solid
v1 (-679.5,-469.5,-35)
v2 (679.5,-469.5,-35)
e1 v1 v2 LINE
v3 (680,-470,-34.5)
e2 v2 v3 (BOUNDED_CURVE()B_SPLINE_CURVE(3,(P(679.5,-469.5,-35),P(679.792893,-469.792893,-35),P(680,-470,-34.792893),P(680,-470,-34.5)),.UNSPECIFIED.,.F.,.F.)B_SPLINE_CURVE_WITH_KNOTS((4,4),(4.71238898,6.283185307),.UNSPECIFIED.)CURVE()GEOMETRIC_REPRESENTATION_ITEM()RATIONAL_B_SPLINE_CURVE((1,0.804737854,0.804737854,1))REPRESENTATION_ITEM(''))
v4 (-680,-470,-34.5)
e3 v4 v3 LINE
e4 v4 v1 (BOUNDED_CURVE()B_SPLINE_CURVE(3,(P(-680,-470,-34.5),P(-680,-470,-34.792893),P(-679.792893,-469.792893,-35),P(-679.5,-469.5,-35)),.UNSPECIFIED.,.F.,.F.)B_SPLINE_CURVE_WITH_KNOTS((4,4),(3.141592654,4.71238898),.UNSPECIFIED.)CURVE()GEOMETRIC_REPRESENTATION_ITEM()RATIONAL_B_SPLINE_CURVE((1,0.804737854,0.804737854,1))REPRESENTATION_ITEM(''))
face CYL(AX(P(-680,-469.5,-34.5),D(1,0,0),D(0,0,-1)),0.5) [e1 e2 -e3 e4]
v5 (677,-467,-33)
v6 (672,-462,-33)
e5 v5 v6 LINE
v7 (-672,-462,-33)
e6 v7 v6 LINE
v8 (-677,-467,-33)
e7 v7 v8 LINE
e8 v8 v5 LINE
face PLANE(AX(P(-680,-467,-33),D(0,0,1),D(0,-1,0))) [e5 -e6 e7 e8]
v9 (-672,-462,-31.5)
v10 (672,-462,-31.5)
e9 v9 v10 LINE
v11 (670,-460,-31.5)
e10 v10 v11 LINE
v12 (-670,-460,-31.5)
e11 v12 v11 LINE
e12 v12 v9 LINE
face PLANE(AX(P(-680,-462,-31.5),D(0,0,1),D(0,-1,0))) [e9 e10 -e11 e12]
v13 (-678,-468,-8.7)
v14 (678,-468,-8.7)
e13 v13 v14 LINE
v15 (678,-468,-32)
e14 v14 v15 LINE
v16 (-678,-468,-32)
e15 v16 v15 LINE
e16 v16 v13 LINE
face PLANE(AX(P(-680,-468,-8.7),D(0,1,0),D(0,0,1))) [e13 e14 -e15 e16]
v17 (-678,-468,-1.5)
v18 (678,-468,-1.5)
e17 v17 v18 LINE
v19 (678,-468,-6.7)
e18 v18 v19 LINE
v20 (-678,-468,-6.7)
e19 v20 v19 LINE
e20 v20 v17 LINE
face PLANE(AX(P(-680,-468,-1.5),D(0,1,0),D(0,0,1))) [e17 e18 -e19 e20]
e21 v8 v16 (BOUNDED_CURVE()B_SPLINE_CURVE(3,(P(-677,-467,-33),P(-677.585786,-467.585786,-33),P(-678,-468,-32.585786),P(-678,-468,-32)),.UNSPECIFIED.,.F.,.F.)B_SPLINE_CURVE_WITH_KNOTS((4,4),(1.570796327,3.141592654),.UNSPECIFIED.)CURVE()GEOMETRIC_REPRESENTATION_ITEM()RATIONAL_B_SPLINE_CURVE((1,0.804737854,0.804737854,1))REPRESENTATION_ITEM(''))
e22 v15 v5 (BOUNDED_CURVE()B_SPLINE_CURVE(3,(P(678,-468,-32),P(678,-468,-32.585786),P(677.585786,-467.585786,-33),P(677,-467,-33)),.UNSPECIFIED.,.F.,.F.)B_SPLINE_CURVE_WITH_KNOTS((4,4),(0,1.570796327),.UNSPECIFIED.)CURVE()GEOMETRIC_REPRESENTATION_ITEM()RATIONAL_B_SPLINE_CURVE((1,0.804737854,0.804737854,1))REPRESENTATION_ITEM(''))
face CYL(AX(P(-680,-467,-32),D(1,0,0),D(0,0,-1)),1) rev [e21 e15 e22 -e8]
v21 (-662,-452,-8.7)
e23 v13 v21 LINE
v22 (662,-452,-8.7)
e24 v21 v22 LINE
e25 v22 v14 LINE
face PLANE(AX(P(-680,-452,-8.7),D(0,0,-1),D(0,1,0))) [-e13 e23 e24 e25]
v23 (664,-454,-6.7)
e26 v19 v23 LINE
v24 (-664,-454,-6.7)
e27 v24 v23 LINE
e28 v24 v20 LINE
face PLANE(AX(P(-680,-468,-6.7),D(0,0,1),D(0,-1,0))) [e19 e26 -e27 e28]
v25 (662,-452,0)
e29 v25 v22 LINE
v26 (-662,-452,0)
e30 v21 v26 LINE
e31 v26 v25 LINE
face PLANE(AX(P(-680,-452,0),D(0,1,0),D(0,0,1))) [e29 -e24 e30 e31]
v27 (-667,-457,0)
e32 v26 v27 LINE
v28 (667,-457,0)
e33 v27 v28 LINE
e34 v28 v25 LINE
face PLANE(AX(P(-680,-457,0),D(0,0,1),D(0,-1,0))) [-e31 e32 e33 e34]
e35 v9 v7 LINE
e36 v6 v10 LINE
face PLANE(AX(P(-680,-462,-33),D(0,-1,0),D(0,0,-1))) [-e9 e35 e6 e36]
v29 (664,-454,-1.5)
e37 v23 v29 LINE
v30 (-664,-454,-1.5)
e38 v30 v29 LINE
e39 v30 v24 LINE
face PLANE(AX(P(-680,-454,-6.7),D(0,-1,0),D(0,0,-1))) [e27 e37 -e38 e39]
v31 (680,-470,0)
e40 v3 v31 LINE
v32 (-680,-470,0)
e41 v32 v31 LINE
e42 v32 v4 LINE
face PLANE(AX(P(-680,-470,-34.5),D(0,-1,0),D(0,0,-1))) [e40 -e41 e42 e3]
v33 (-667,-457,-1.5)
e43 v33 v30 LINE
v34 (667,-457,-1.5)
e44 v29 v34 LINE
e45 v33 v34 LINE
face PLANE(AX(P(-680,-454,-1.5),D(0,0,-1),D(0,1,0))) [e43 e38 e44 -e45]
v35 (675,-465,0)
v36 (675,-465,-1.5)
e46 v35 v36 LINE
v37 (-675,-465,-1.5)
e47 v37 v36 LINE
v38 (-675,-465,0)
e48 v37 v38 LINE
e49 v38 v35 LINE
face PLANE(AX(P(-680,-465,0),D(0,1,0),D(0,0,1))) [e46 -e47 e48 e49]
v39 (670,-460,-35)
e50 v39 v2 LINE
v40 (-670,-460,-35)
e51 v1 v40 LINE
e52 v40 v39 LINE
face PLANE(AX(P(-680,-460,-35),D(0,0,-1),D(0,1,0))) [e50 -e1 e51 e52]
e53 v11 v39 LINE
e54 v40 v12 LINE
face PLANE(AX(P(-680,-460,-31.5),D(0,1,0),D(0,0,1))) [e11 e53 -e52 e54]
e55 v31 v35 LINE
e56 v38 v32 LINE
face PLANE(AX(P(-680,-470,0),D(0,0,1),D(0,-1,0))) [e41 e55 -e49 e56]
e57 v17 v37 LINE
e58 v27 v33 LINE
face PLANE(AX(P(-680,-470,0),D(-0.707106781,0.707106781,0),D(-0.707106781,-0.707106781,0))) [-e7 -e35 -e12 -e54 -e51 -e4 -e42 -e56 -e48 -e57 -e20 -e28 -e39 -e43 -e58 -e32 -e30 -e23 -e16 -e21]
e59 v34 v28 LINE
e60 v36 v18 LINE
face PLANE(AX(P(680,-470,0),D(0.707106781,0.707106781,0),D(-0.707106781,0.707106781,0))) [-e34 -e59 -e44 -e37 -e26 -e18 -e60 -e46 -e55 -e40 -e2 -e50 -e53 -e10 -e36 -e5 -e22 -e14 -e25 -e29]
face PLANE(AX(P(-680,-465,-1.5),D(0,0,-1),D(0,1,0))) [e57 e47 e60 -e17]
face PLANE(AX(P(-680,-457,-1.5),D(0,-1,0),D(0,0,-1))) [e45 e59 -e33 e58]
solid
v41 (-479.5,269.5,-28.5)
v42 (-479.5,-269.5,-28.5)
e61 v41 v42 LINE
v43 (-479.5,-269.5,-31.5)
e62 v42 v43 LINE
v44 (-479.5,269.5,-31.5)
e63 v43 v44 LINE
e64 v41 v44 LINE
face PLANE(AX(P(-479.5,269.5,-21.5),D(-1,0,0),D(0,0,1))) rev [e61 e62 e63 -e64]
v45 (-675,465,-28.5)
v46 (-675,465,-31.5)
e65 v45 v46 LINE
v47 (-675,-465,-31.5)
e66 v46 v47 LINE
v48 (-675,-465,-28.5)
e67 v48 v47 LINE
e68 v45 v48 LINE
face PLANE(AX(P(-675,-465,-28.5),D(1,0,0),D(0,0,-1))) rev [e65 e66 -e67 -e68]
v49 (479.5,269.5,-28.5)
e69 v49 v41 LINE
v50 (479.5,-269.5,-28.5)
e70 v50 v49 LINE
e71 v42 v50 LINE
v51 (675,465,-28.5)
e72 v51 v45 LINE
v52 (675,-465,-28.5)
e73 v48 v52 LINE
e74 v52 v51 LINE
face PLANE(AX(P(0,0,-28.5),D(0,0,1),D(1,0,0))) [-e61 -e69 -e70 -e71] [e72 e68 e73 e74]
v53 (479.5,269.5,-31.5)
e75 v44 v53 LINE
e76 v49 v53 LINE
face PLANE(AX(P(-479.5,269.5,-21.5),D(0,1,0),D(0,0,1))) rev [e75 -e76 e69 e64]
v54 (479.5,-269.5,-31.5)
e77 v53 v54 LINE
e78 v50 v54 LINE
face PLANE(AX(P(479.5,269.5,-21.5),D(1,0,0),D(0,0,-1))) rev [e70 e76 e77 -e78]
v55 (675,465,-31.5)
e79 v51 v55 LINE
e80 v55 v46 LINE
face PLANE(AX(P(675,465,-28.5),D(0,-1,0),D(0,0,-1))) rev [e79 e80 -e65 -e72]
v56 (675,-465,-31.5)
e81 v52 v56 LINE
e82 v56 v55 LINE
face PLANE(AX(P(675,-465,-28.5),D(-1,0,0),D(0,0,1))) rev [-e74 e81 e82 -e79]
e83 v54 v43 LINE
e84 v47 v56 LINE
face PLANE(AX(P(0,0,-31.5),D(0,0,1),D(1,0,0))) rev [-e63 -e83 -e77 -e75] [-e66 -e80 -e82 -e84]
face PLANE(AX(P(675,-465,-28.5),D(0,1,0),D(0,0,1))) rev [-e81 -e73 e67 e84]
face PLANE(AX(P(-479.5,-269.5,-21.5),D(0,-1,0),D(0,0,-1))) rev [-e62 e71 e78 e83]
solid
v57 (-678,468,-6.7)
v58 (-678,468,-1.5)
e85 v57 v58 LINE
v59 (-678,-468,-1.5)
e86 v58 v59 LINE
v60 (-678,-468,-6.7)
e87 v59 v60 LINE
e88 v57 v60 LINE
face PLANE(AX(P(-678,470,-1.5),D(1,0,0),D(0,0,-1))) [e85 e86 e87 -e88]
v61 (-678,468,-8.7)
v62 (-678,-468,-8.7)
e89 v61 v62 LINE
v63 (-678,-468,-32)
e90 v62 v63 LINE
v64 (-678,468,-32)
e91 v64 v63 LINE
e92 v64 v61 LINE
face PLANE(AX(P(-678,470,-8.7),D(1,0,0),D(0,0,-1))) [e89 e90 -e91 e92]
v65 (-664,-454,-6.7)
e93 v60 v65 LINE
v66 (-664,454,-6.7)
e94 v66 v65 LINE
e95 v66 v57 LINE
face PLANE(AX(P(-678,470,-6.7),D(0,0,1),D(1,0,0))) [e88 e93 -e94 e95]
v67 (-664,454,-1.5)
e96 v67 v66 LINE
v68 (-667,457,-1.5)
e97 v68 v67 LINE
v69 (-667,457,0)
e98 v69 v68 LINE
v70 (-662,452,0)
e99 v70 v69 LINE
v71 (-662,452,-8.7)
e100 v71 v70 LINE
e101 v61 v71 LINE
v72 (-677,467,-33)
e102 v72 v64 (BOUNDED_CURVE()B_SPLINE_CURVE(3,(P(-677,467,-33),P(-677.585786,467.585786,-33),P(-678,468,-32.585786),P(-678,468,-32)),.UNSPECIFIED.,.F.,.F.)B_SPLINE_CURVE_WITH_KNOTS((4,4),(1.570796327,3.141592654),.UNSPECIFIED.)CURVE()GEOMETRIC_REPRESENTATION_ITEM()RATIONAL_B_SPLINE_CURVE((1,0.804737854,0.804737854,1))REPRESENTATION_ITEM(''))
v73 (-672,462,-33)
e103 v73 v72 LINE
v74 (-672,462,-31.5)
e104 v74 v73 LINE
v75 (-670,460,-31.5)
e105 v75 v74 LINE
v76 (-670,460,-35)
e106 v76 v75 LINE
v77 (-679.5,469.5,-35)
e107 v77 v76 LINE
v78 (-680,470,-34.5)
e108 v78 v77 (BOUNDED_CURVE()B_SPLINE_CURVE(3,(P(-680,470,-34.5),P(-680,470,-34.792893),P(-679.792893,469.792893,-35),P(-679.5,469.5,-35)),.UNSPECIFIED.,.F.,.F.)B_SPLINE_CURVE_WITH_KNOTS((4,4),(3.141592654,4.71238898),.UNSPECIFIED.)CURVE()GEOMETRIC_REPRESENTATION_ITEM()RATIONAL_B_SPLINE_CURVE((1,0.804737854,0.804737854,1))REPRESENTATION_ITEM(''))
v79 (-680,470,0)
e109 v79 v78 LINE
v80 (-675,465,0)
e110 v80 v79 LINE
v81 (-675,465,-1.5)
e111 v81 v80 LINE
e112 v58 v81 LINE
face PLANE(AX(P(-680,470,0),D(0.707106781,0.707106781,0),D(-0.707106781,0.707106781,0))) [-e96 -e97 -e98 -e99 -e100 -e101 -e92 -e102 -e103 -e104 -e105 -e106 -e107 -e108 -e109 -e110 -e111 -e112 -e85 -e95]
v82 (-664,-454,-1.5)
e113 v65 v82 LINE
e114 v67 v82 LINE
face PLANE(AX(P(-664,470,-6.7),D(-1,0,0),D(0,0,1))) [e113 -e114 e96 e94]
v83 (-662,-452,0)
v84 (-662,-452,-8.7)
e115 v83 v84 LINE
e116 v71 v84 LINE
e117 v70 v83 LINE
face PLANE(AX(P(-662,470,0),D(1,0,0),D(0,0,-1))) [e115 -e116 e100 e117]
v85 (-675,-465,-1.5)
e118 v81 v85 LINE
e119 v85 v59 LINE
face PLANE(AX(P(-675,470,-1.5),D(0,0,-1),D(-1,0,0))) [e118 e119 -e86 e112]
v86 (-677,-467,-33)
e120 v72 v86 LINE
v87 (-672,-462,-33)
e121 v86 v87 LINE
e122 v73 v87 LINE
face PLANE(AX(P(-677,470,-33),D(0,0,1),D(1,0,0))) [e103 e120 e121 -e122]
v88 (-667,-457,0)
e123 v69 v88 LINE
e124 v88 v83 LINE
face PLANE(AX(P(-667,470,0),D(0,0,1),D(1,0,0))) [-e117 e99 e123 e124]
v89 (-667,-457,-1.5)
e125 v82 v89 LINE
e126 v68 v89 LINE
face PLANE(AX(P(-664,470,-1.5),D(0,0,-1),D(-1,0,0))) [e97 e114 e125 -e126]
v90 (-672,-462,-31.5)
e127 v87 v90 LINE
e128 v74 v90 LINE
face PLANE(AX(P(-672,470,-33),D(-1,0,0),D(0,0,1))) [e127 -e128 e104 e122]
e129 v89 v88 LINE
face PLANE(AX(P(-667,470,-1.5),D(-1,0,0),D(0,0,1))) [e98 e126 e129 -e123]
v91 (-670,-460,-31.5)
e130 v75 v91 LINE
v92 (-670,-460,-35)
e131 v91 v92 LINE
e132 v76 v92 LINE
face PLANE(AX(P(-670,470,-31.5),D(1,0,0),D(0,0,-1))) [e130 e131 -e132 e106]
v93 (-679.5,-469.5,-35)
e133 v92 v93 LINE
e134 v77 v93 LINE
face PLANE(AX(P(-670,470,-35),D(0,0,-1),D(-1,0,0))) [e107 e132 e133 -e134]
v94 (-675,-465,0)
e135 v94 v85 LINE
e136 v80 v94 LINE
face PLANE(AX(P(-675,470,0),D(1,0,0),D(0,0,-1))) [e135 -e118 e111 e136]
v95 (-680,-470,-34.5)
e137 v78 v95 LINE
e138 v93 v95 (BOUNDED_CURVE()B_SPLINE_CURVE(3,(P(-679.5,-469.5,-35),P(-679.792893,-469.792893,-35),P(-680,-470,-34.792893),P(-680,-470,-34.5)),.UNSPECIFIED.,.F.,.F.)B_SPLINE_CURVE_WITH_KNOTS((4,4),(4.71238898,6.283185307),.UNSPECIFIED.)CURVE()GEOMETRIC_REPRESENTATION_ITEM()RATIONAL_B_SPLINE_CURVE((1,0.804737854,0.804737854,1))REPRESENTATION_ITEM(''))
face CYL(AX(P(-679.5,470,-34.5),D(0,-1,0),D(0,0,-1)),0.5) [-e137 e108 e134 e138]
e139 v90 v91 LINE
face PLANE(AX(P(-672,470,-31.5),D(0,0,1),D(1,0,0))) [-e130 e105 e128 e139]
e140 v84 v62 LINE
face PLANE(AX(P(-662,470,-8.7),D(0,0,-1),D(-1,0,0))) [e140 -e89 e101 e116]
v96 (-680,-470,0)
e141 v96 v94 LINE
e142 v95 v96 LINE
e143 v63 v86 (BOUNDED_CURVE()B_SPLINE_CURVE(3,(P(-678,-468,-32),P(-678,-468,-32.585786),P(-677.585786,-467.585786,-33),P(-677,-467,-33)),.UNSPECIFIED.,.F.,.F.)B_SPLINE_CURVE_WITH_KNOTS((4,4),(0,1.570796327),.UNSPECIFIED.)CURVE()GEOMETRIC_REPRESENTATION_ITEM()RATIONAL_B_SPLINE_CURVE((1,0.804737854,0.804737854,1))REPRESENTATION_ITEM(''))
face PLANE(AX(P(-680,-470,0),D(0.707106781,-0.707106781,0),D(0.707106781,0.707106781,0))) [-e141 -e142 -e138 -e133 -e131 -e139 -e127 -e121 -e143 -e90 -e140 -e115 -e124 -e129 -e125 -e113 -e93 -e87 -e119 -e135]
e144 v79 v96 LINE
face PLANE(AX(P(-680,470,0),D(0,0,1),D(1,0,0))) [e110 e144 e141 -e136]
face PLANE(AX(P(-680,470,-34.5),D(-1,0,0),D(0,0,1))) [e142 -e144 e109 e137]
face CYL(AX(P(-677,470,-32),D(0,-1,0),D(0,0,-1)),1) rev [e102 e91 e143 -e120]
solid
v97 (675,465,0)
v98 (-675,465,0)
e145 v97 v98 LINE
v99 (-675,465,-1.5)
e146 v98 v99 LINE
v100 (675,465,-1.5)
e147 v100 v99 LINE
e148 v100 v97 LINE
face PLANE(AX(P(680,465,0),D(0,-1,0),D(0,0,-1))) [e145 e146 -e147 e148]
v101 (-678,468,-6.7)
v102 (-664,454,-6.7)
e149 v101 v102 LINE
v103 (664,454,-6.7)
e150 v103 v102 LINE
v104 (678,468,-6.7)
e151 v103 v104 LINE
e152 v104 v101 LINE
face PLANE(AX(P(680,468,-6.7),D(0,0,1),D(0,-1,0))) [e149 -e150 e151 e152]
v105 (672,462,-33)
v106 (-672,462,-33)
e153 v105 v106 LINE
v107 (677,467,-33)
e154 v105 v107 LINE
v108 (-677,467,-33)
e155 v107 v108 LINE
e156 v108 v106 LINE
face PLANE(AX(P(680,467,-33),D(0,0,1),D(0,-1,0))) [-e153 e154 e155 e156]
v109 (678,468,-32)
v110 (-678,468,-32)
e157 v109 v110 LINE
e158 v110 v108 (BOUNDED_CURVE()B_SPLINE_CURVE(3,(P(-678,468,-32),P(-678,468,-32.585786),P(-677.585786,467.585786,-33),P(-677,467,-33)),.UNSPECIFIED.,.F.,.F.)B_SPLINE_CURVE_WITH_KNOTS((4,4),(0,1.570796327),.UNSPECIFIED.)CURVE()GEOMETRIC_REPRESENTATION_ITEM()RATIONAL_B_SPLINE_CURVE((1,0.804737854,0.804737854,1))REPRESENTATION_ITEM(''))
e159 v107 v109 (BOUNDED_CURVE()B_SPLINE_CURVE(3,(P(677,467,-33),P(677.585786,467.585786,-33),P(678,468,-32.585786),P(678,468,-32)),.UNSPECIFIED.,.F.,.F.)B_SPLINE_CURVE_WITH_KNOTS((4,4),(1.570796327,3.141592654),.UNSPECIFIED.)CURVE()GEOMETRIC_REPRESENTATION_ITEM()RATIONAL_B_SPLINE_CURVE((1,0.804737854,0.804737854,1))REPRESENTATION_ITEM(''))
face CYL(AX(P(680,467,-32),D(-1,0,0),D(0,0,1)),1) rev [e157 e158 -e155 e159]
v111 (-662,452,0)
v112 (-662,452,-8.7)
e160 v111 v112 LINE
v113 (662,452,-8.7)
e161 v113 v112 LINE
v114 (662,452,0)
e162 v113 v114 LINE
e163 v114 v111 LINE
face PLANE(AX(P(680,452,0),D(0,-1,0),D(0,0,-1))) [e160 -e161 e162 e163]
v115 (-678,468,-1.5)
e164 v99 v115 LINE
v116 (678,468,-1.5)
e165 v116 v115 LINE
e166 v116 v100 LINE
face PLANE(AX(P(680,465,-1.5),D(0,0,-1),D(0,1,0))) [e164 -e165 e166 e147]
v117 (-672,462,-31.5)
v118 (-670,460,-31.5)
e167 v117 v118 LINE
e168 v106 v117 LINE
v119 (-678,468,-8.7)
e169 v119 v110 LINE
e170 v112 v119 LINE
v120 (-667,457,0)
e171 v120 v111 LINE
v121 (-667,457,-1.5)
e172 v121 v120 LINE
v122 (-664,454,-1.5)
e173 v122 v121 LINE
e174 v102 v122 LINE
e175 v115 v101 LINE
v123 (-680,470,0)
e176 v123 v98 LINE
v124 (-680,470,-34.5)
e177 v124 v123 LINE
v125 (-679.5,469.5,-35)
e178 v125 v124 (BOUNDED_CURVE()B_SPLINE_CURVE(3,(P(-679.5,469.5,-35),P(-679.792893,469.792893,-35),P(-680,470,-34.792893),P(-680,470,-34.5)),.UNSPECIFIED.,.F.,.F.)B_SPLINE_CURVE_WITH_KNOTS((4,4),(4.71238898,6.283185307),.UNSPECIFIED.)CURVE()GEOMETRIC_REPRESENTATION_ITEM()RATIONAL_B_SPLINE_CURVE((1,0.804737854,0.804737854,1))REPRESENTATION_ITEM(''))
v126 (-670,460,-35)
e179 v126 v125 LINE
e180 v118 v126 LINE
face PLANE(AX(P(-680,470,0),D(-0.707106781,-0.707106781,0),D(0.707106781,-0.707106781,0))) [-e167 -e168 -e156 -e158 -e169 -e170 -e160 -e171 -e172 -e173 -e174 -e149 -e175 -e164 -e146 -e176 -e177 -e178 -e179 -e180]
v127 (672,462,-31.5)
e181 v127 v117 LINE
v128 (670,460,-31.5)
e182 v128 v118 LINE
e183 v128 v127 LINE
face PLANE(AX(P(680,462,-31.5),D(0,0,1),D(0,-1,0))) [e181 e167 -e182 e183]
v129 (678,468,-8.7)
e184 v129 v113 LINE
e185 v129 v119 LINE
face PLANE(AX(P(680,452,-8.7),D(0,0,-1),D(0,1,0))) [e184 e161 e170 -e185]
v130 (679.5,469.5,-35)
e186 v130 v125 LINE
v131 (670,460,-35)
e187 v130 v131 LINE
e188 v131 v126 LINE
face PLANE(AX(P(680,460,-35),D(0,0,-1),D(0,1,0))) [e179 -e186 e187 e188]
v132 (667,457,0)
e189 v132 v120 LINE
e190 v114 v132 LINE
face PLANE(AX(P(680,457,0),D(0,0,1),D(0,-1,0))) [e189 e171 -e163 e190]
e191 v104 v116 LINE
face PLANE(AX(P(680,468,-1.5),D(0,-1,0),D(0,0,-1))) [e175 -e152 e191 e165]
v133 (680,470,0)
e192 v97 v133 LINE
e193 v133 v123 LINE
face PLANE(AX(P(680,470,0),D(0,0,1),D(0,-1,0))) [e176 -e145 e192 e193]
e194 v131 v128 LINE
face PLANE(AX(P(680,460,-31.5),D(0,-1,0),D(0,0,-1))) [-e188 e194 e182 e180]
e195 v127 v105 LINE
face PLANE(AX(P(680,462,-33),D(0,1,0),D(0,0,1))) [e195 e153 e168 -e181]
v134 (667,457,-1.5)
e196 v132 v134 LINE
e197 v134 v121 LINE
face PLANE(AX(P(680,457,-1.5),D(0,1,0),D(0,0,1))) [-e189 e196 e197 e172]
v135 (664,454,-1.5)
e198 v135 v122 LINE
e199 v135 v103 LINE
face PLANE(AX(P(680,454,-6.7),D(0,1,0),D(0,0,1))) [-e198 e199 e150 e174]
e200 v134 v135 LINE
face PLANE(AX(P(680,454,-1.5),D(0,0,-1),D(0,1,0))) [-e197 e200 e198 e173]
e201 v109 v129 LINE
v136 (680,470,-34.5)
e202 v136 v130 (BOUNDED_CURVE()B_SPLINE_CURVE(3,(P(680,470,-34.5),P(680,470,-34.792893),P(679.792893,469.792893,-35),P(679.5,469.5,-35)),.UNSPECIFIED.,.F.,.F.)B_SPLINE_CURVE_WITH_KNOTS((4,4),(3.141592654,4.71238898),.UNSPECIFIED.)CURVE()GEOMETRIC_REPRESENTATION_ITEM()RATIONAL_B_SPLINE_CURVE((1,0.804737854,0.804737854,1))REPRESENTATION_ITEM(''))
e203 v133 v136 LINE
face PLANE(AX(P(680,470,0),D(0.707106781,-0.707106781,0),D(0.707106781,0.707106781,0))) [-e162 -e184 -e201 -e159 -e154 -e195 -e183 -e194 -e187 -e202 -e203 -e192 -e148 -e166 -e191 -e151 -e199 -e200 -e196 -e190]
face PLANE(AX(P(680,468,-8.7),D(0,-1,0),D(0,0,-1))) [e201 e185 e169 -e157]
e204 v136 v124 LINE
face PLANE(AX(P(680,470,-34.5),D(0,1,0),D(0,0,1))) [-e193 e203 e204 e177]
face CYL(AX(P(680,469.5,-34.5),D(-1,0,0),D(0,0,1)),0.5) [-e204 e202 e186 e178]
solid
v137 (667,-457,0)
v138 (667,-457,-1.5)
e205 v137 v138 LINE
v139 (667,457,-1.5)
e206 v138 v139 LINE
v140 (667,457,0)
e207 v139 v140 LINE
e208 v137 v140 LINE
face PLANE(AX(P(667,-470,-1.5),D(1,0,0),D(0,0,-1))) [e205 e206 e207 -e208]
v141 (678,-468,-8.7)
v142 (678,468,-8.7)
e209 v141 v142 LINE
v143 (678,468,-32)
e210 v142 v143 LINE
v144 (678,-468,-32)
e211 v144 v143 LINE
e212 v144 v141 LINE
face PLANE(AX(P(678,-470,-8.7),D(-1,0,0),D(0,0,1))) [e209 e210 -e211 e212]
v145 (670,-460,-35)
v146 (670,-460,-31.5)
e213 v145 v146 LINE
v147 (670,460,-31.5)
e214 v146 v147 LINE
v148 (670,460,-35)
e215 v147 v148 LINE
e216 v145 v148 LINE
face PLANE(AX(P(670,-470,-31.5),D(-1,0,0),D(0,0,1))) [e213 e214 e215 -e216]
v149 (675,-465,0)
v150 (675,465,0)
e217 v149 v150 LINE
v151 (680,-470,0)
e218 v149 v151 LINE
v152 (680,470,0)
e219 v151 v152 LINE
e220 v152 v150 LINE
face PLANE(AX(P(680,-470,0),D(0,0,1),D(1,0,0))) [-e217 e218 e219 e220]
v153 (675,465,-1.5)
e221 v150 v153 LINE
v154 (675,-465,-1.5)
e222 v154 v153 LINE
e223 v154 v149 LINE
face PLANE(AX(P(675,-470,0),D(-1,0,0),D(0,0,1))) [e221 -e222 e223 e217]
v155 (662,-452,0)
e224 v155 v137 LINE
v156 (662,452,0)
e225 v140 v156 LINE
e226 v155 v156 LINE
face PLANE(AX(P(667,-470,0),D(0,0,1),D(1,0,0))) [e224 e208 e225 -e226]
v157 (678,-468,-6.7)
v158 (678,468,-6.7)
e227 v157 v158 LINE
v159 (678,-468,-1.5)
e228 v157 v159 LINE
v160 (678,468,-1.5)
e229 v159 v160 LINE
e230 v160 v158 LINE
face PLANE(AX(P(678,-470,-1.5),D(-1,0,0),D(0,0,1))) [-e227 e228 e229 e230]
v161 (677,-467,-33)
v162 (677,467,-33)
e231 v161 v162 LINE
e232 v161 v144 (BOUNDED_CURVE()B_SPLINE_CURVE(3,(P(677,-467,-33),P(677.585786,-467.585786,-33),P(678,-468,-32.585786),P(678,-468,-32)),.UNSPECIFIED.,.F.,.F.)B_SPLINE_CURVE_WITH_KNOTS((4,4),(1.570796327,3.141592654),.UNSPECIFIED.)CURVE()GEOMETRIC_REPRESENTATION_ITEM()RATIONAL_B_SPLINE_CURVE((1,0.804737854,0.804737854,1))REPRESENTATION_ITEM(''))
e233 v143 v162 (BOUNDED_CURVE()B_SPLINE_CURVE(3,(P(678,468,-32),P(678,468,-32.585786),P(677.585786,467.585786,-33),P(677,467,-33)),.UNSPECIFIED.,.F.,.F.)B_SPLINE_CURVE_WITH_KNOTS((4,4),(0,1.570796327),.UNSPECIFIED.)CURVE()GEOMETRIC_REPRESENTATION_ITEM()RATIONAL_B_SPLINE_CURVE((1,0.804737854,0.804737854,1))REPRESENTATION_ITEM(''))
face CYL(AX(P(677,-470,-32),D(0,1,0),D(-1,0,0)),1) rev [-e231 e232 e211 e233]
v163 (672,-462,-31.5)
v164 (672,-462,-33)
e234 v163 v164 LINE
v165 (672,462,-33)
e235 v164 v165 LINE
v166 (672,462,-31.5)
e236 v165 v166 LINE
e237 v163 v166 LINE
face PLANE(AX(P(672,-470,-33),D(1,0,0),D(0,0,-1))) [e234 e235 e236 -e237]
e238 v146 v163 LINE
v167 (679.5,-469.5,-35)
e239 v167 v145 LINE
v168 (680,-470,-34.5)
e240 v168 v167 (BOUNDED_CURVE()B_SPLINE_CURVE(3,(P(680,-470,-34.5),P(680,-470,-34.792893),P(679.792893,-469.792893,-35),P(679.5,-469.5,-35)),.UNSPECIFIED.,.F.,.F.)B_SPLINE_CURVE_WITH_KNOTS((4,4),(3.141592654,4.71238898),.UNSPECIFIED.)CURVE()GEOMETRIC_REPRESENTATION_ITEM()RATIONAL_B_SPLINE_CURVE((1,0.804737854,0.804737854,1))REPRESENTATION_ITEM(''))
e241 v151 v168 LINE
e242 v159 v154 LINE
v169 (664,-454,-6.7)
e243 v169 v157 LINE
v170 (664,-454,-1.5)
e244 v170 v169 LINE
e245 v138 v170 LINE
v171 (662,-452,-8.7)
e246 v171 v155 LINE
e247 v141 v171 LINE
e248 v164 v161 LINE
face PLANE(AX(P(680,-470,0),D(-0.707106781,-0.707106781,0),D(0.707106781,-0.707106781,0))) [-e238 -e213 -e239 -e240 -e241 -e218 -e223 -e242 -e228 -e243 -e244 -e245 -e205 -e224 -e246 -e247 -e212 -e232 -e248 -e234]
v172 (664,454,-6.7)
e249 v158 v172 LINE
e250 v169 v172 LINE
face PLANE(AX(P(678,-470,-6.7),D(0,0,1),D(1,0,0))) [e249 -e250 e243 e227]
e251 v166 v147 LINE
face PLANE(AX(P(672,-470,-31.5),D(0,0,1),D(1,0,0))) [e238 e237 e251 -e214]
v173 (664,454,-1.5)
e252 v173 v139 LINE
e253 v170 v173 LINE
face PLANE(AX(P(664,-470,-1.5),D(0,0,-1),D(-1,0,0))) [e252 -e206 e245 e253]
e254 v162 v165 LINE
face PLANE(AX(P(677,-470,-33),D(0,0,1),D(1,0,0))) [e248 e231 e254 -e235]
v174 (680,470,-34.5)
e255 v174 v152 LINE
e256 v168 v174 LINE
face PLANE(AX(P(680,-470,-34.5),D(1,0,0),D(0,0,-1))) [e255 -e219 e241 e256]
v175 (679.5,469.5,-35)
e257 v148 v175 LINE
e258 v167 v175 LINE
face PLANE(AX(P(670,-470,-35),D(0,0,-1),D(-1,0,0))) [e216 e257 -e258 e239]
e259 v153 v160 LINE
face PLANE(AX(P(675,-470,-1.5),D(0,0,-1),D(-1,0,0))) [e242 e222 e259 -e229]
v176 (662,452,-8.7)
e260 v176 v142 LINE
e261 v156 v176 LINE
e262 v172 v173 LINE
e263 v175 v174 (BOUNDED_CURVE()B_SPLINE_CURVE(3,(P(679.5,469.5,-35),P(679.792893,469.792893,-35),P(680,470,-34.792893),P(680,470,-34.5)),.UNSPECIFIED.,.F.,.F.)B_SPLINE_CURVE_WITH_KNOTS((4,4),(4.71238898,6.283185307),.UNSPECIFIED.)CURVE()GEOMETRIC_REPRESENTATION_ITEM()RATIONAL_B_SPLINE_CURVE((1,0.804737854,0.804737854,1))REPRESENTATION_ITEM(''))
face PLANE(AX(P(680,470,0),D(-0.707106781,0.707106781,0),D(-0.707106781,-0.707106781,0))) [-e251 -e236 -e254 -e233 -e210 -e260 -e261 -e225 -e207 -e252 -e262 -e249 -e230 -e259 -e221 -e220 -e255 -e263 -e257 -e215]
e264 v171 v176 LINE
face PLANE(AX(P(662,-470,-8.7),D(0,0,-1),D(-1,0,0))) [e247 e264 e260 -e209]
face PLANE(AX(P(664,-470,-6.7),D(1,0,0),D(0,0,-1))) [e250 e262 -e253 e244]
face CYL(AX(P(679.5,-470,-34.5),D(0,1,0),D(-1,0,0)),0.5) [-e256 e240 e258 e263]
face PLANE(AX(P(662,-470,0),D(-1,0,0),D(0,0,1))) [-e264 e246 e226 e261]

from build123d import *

# Parameters (mm, degrees)
MEMBER_1_DEPTH      = 40.357337308
MEMBER_1_DEPTH_BACK = 1400.357337308
MEMBER_1_2_DEPTH    = 1020.714674617
MEMBER_1_3_DEPTH    = 1440.714674617
MEMBER_1_4_DEPTH    = 1020.714674617
SKETCH_12_W         = 1350
SKETCH_12_H         = 930
EXTRUDE_1_DEPTH     = 3
SKETCH_13_W         = 959
SKETCH_13_H         = 539
CUT_EXTRUDE_1_DEPTH = 10


with BuildPart() as part:
    # 草图11 → Member 1 (new, two sides: drawn at the far end of the back side and taken through both)
    with BuildSketch(Plane(origin=(-680, 470, 0), x_dir=(0, -1, 0), z_dir=(-1, 0, 0)).offset(-MEMBER_1_DEPTH_BACK)):
        with BuildLine():
            Line((13, -1.5), (13, 0))
            Line((13, 0), (18, 0))
            Line((18, 0), (18, -8.7))
            Line((18, -8.7), (2, -8.7))
            Line((2, -8.7), (2, -32))
            ThreePointArc((2, -32), (2.292893219, -32.707106781), (3, -33))
            Line((3, -33), (8, -33))
            Line((8, -33), (8, -31.5))
            Line((8, -31.5), (10, -31.5))
            Line((10, -31.5), (10, -35))
            Line((10, -35), (0.5, -35))
            ThreePointArc((0.5, -35), (0.146446609, -34.853553391), (0, -34.5))
            Line((0, -34.5), (0, 0))
            Line((0, 0), (5, 0))
            Line((5, 0), (5, -1.5))
            Line((5, -1.5), (2, -1.5))
            Line((2, -1.5), (2, -6.7))
            Line((2, -6.7), (16, -6.7))
            Line((16, -6.7), (16, -1.5))
            Line((16, -1.5), (13, -1.5))
        make_face()
    extrude(amount=MEMBER_1_DEPTH + MEMBER_1_DEPTH_BACK)

    # Member 1 mitre 1
    split(bisect_by=Plane(origin=(-680, 470, 0), x_dir=(-0.707106781, 0.707106781, 0), z_dir=(0.707106781, 0.707106781, 0)), keep=Keep.TOP)

    # Member 1 mitre 2
    split(bisect_by=Plane(origin=(680, 470, 0), x_dir=(-0.707106781, -0.707106781, 0), z_dir=(-0.707106781, 0.707106781, 0)), keep=Keep.TOP)


with BuildPart() as body_2:
    # 草图11 on segment 2 (carried to segment 2) → Member 1 2 (new body)
    with BuildSketch(Plane(origin=(680, -510.357337308, 0), x_dir=(-1, 0, 0), z_dir=(0, 1, 0))):
        with BuildLine():
            Line((13, -1.5), (13, 0))
            Line((13, 0), (18, 0))
            Line((18, 0), (18, -8.7))
            Line((18, -8.7), (2, -8.7))
            Line((2, -8.7), (2, -32))
            ThreePointArc((2, -32), (2.292893219, -32.707106781), (3, -33))
            Line((3, -33), (8, -33))
            Line((8, -33), (8, -31.5))
            Line((8, -31.5), (10, -31.5))
            Line((10, -31.5), (10, -35))
            Line((10, -35), (0.5, -35))
            ThreePointArc((0.5, -35), (0.146446609, -34.853553391), (0, -34.5))
            Line((0, -34.5), (0, 0))
            Line((0, 0), (5, 0))
            Line((5, 0), (5, -1.5))
            Line((5, -1.5), (2, -1.5))
            Line((2, -1.5), (2, -6.7))
            Line((2, -6.7), (16, -6.7))
            Line((16, -6.7), (16, -1.5))
            Line((16, -1.5), (13, -1.5))
        make_face()
    extrude(amount=MEMBER_1_2_DEPTH)

    # Member 1 2 mitre 1
    split(bisect_by=Plane(origin=(680, 470, 0), x_dir=(0.707106781, 0.707106781, 0), z_dir=(0.707106781, -0.707106781, 0)), keep=Keep.TOP)

    # Member 1 2 mitre 2
    split(bisect_by=Plane(origin=(680, -470, 0), x_dir=(-0.707106781, 0.707106781, 0), z_dir=(0.707106781, 0.707106781, 0)), keep=Keep.TOP)


with BuildPart() as body_3:
    # 草图11 on segment 3 (carried to segment 3) → Member 1 3 (new body)
    with BuildSketch(Plane(origin=(-720.357337308, -470, 0), x_dir=(0, 1, 0), z_dir=(1, 0, 0))):
        with BuildLine():
            Line((13, -1.5), (13, 0))
            Line((13, 0), (18, 0))
            Line((18, 0), (18, -8.7))
            Line((18, -8.7), (2, -8.7))
            Line((2, -8.7), (2, -32))
            ThreePointArc((2, -32), (2.292893219, -32.707106781), (3, -33))
            Line((3, -33), (8, -33))
            Line((8, -33), (8, -31.5))
            Line((8, -31.5), (10, -31.5))
            Line((10, -31.5), (10, -35))
            Line((10, -35), (0.5, -35))
            ThreePointArc((0.5, -35), (0.146446609, -34.853553391), (0, -34.5))
            Line((0, -34.5), (0, 0))
            Line((0, 0), (5, 0))
            Line((5, 0), (5, -1.5))
            Line((5, -1.5), (2, -1.5))
            Line((2, -1.5), (2, -6.7))
            Line((2, -6.7), (16, -6.7))
            Line((16, -6.7), (16, -1.5))
            Line((16, -1.5), (13, -1.5))
        make_face()
    extrude(amount=MEMBER_1_3_DEPTH)

    # Member 1 3 mitre 1
    split(bisect_by=Plane(origin=(-680, -470, 0), x_dir=(0.707106781, 0.707106781, 0), z_dir=(0.707106781, -0.707106781, 0)), keep=Keep.TOP)

    # Member 1 3 mitre 2
    split(bisect_by=Plane(origin=(680, -470, 0), x_dir=(0.707106781, -0.707106781, 0), z_dir=(-0.707106781, -0.707106781, 0)), keep=Keep.TOP)


with BuildPart() as body_4:
    # 草图11 on segment 4 (carried to segment 4) → Member 1 4 (new body)
    with BuildSketch(Plane(origin=(-680, 510.357337308, 0), x_dir=(1, 0, 0), z_dir=(0, -1, 0))):
        with BuildLine():
            Line((13, -1.5), (13, 0))
            Line((13, 0), (18, 0))
            Line((18, 0), (18, -8.7))
            Line((18, -8.7), (2, -8.7))
            Line((2, -8.7), (2, -32))
            ThreePointArc((2, -32), (2.292893219, -32.707106781), (3, -33))
            Line((3, -33), (8, -33))
            Line((8, -33), (8, -31.5))
            Line((8, -31.5), (10, -31.5))
            Line((10, -31.5), (10, -35))
            Line((10, -35), (0.5, -35))
            ThreePointArc((0.5, -35), (0.146446609, -34.853553391), (0, -34.5))
            Line((0, -34.5), (0, 0))
            Line((0, 0), (5, 0))
            Line((5, 0), (5, -1.5))
            Line((5, -1.5), (2, -1.5))
            Line((2, -1.5), (2, -6.7))
            Line((2, -6.7), (16, -6.7))
            Line((16, -6.7), (16, -1.5))
            Line((16, -1.5), (13, -1.5))
        make_face()
    extrude(amount=MEMBER_1_4_DEPTH)

    # Member 1 4 mitre 1
    split(bisect_by=Plane(origin=(-680, 470, 0), x_dir=(0.707106781, -0.707106781, 0), z_dir=(-0.707106781, -0.707106781, 0)), keep=Keep.TOP)

    # Member 1 4 mitre 2
    split(bisect_by=Plane(origin=(-680, -470, 0), x_dir=(-0.707106781, -0.707106781, 0), z_dir=(-0.707106781, 0.707106781, 0)), keep=Keep.TOP)


with BuildPart() as body_5:
    # 草图12 → 凸台-拉伸1 (new body)
    with BuildSketch(Plane.XY.offset(-31.5)):
        Rectangle(SKETCH_12_W, SKETCH_12_H)
    extrude(amount=EXTRUDE_1_DEPTH)

    # 草图13 → 切除-拉伸1 (cut)
    with BuildSketch(Plane(origin=(0, 0, -31.5), x_dir=(-1, 0, 0), z_dir=(0, 0, -1))):
        Rectangle(SKETCH_13_W, SKETCH_13_H)
    extrude(amount=-CUT_EXTRUDE_1_DEPTH, mode=Mode.SUBTRACT)


solid = Compound([part.part, body_2.part, body_3.part, body_4.part, body_5.part])
